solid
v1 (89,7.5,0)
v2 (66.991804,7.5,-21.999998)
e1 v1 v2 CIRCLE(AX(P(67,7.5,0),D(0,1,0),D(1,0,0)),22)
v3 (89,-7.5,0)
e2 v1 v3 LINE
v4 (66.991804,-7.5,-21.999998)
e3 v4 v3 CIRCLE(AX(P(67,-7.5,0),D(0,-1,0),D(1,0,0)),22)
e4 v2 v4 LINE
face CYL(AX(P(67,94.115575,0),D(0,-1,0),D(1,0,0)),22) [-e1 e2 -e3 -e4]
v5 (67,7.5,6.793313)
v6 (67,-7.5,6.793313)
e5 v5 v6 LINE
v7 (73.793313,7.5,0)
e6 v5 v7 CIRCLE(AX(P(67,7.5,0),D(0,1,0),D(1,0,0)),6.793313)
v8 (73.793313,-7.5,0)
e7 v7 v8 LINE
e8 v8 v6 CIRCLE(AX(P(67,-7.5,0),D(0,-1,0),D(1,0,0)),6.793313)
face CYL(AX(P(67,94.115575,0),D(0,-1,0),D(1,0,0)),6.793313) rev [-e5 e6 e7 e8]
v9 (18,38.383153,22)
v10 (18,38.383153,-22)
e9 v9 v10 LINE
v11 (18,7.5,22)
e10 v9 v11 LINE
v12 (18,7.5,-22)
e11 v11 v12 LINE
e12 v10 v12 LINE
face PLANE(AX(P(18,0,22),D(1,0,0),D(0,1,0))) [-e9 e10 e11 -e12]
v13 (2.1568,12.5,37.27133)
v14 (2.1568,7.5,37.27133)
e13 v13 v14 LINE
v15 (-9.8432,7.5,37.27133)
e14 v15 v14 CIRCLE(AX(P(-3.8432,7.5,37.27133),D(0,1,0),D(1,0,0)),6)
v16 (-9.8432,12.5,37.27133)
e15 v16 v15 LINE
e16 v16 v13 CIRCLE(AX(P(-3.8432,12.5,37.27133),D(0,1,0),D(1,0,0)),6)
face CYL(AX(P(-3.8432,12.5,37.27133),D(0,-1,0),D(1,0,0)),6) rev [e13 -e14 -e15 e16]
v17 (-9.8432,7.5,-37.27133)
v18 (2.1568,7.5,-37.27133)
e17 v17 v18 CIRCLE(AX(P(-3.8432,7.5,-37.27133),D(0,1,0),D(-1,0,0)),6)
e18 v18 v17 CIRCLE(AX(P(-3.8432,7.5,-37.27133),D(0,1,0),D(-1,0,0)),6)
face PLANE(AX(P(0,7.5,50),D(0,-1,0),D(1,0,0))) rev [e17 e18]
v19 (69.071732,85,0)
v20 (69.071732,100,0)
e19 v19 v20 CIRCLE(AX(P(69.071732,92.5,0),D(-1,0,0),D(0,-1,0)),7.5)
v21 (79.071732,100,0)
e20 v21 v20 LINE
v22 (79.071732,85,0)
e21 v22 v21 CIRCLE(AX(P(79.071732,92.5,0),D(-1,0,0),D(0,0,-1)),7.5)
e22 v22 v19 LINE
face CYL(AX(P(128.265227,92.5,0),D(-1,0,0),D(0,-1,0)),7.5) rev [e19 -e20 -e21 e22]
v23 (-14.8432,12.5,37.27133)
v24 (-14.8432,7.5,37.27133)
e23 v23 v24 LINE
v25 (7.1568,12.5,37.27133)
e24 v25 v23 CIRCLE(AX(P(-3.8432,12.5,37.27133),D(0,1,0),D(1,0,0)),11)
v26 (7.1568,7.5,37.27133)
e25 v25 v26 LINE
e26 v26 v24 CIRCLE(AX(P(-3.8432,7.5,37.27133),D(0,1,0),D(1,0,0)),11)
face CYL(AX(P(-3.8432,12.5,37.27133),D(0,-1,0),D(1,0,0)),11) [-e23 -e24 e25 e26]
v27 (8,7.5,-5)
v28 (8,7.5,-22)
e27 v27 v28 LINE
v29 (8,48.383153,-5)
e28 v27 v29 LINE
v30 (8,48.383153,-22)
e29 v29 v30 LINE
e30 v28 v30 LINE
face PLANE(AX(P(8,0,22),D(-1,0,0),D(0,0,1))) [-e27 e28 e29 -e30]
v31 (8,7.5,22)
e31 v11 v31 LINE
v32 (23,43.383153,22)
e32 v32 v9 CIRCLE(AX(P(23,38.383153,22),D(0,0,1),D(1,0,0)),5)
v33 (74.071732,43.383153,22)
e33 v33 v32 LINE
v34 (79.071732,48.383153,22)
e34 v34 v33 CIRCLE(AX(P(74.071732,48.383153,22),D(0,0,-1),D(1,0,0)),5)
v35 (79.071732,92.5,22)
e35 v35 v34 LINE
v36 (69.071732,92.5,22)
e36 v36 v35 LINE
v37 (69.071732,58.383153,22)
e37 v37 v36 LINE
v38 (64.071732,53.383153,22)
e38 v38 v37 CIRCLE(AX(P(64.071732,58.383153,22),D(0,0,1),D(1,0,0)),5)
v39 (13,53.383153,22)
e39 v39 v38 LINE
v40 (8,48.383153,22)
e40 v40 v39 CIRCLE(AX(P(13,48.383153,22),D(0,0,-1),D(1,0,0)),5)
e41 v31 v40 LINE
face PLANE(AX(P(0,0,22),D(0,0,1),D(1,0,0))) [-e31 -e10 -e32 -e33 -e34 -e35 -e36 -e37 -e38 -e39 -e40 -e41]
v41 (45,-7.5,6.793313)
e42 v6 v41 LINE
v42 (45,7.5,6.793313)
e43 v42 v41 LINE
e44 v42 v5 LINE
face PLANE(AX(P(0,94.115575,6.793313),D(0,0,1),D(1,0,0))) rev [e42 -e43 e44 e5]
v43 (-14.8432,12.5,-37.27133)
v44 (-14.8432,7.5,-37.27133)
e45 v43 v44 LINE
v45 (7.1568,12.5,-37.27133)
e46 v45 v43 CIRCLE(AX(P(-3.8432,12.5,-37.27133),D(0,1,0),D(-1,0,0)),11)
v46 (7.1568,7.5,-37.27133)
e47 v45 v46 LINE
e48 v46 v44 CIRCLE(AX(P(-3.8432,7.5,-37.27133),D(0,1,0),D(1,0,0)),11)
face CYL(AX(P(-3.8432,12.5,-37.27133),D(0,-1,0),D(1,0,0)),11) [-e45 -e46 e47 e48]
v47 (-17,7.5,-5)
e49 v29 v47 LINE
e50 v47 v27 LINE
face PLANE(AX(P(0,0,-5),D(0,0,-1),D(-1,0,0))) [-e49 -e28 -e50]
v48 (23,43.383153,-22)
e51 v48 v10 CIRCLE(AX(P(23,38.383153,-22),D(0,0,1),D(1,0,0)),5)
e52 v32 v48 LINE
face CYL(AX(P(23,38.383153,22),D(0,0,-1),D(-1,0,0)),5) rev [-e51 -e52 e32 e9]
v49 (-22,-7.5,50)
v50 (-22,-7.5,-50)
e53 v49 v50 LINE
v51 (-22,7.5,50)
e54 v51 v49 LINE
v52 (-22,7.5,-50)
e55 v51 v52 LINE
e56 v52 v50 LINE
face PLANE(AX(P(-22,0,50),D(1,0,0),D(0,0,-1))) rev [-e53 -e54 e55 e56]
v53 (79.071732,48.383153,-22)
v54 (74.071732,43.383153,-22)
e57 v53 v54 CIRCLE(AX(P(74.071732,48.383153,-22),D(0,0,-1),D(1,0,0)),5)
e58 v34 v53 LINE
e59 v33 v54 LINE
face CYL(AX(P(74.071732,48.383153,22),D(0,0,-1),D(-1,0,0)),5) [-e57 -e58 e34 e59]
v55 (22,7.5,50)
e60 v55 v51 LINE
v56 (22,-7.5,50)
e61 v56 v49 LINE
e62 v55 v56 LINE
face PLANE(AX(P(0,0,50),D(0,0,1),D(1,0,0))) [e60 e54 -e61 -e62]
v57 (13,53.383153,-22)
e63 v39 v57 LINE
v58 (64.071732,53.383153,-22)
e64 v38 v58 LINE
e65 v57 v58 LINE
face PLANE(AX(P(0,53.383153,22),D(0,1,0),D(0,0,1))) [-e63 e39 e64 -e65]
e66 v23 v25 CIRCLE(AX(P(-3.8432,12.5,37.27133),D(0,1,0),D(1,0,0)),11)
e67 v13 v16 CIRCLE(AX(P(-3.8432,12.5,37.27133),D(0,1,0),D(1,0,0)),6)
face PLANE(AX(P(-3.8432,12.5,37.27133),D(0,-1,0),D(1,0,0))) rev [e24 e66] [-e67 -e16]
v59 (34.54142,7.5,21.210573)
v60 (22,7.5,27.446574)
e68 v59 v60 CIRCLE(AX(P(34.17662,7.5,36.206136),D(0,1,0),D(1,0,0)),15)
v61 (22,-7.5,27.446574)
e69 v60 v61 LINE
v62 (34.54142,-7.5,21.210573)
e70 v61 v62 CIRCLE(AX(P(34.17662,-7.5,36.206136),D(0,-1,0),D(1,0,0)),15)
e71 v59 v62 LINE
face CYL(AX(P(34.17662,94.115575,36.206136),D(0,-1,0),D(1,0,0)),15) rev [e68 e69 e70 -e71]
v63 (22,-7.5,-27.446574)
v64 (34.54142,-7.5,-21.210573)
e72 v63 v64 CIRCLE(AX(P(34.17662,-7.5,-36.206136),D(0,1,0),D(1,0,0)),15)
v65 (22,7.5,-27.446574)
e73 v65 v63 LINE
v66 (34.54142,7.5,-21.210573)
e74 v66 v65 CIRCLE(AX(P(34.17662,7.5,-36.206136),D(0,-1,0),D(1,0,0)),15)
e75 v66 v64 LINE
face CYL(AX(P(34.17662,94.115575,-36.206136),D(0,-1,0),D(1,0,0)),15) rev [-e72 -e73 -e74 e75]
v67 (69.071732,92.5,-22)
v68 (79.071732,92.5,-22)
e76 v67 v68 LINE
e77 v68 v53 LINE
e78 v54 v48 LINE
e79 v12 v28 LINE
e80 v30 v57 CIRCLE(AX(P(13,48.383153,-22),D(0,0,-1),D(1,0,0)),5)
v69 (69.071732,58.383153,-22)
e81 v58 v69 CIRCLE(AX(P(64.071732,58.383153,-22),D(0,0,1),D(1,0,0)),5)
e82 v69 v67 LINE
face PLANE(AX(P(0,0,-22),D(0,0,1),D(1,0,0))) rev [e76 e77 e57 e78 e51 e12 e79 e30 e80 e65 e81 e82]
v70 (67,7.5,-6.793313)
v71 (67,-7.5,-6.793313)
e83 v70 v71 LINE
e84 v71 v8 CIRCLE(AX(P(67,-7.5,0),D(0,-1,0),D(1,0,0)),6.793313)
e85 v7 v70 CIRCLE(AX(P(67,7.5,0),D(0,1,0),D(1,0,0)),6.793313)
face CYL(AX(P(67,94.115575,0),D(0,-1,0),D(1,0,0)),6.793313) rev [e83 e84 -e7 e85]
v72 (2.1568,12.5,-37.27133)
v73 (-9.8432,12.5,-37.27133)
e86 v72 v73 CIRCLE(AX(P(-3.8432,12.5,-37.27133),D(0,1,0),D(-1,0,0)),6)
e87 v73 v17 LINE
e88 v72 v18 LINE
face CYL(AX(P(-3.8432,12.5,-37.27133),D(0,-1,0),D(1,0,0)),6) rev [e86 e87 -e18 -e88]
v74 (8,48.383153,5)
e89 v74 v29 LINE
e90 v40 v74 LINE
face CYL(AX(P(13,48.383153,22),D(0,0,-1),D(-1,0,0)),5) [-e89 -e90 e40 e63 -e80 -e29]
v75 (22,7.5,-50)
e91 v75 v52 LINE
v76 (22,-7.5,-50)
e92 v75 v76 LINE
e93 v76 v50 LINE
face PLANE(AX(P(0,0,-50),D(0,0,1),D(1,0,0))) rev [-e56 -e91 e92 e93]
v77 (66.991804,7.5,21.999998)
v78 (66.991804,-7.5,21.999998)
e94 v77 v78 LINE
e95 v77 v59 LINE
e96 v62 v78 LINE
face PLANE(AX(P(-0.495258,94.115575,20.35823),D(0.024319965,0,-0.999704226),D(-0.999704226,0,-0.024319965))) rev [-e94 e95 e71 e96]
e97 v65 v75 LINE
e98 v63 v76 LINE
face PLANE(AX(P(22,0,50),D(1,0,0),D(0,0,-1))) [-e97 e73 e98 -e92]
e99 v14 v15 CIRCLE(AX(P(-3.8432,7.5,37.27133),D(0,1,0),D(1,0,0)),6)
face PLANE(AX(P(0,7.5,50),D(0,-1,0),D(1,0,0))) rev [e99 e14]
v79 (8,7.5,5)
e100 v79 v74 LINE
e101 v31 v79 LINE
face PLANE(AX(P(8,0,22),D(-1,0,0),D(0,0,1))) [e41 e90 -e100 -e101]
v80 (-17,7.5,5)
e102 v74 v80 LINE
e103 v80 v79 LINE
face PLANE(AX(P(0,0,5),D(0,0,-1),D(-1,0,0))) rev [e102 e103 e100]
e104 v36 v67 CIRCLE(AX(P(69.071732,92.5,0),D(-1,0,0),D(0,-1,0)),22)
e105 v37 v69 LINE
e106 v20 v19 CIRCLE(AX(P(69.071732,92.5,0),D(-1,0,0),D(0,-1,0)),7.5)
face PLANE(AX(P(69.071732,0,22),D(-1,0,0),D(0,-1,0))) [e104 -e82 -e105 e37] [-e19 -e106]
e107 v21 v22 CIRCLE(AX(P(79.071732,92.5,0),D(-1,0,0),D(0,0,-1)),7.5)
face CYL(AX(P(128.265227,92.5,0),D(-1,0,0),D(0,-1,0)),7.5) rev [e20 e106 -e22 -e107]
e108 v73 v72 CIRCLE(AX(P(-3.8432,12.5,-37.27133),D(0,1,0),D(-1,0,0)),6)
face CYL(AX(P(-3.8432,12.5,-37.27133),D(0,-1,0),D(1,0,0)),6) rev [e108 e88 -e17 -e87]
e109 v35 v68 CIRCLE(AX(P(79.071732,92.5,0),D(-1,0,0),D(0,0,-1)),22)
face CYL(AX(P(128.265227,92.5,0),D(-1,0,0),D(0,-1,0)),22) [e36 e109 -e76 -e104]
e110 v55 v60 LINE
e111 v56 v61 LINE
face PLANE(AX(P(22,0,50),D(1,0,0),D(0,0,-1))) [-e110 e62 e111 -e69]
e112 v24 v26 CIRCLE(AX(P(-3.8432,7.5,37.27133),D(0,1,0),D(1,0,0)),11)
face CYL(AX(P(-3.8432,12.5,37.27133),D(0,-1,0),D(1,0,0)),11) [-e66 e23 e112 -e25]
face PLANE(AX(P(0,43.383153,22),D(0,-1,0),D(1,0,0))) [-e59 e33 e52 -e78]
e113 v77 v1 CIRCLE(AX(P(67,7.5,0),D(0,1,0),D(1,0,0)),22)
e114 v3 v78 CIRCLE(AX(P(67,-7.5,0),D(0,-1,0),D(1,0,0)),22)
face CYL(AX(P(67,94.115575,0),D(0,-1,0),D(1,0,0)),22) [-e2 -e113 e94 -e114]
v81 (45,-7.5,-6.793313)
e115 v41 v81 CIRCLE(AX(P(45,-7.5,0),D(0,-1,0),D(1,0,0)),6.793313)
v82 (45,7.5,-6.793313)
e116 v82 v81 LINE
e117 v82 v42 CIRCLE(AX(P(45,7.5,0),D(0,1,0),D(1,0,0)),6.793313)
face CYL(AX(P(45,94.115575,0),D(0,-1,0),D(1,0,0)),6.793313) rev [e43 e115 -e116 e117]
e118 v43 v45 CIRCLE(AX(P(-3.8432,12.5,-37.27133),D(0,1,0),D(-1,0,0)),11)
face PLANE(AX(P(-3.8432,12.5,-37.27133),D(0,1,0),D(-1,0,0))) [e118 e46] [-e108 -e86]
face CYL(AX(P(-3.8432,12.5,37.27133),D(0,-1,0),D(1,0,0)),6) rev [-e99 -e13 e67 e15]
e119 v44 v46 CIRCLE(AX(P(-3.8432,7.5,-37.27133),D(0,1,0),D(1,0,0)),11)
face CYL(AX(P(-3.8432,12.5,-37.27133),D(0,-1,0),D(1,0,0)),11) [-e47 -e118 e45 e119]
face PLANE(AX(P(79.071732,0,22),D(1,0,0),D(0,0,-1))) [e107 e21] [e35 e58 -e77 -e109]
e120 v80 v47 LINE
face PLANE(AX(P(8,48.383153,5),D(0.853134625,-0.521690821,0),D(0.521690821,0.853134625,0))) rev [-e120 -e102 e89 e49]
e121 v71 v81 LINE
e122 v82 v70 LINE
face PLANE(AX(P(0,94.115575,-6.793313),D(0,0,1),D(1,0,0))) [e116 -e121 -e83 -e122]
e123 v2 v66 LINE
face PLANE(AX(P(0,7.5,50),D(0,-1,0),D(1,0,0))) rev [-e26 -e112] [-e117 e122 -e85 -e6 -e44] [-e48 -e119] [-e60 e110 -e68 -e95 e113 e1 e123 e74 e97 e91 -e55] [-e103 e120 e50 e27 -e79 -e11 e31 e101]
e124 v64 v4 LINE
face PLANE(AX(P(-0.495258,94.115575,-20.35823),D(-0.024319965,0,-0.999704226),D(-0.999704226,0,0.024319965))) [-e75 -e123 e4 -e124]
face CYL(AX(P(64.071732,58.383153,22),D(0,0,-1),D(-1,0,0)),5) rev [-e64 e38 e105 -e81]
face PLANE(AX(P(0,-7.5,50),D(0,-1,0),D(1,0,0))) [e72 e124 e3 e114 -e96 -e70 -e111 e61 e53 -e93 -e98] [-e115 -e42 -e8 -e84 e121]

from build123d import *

# Parameters (mm, degrees)
BRACKET_PROFILE_SKETCH_W = 44
BRACKET_PROFILE_SKETCH_H = 15
BRACKET_BASE_BODY_DEPTH  = 50
UPRIGHT_WEB_DEPTH        = 22
LUG_BOSS_DEPTH           = 10
LUG_HOLE_CUT_DEPTH       = 44
WASHER_BOSS_SKETCH_R     = 11
WASHER_BOSS_SKETCH_R_2   = 6
WASHER_BOSS_22_DEPTH     = 5
WEB_PAD_DEPTH            = 5
SLOTTED_TAB_DEPTH        = 15


with BuildPart() as part:
    # Bracket Profile Sketch → Bracket Base Body (new, symmetric)
    with BuildSketch(Plane.XY):
        Rectangle(BRACKET_PROFILE_SKETCH_W, BRACKET_PROFILE_SKETCH_H)
    extrude(amount=BRACKET_BASE_BODY_DEPTH, both=True)

    # Sketch1_3 → Upright Web (add, symmetric)
    with BuildSketch(Plane.XY):
        with BuildLine():
            Line((8, 7.5), (18, 7.5))
            Line((18, 7.5), (18, 38.383152955))
            ThreePointArc((18, 38.383152955), (19.464466094, 41.91868686), (23, 43.383152955))
            Line((23, 43.383152955), (74.071731591, 43.383152955))
            ThreePointArc((74.071731591, 43.383152955), (77.607265497, 44.847619049), (79.071731591, 48.383152955))
            Line((79.071731591, 48.383152955), (79.071731591, 92.5))
            Line((79.071731591, 92.5), (69.071731591, 92.5))
            Line((69.071731591, 92.5), (69.071731591, 58.383152955))
            ThreePointArc((69.071731591, 58.383152955), (67.607265497, 54.847619049), (64.071731591, 53.383152955))
            Line((64.071731591, 53.383152955), (13, 53.383152955))
            ThreePointArc((13, 53.383152955), (9.464466094, 51.91868686), (8, 48.383152955))
            Line((8, 48.383152955), (8, 7.5))
        make_face()
    extrude(amount=UPRIGHT_WEB_DEPTH, both=True)

    # Lug Profile Sketch → Lug Boss (add)
    with BuildSketch(Plane.ZY.offset(-69.071731591)):
        with BuildLine():
            Line((7.5, 92.5), (22, 92.5))
            ThreePointArc((22, 92.5), (0, 114.5), (-22, 92.5))
            Line((-22, 92.5), (-7.5, 92.5))
            ThreePointArc((-7.5, 92.5), (0, 100), (7.5, 92.5))
        make_face()
    extrude(amount=-LUG_BOSS_DEPTH)

    # Sketch2_3 → Lug Hole Cut (cut)
    with BuildSketch(Plane.ZY.offset(-69.071731591)):
        with BuildLine():
            ThreePointArc((-7.5, 92.5), (0, 85), (7.5, 92.5))
            Line((7.5, 92.5), (-7.5, 92.5))
        make_face()
        with BuildLine():
            Line((-7.5, 92.5), (7.5, 92.5))
            ThreePointArc((7.5, 92.5), (0, 100), (-7.5, 92.5))
        make_face()
    extrude(amount=-LUG_HOLE_CUT_DEPTH, mode=Mode.SUBTRACT)

    # Washer Boss Sketch → Washer Boss _22 (add)
    # profile 1 of 2: a face of its own
    with BuildSketch(Plane(origin=(0, 7.5, 0), x_dir=(1, 0, 0), z_dir=(0, 1, 0))):
        with Locations((-3.843200035, 37.271330251)):
            Circle(WASHER_BOSS_SKETCH_R)
        with Locations(Location((-3.843200035, 37.271330251, 0), (0, 0, 180))):
            Circle(WASHER_BOSS_SKETCH_R_2, mode=Mode.SUBTRACT)
    # profile 2 of 2: a face of its own
    with BuildSketch(Plane(origin=(0, 7.5, 0), x_dir=(1, 0, 0), z_dir=(0, 1, 0))):
        with Locations((-3.843200035, -37.271330251)):
            Circle(WASHER_BOSS_SKETCH_R)
        with Locations((-3.843200035, -37.271330251)):
            Circle(WASHER_BOSS_SKETCH_R_2, mode=Mode.SUBTRACT)
    extrude(amount=WASHER_BOSS_22_DEPTH)

    # Web Pad Sketch → Web Pad (add, symmetric)
    with BuildSketch(Plane.XY):
        Polygon((8, 48.383152955), (-17, 7.5), (8, 7.5), align=None)
    extrude(amount=WEB_PAD_DEPTH, both=True)

    # Slotted Tab Sketch → Slotted Tab (add)
    with BuildSketch(Plane.XZ.offset(7.5)):
        with BuildLine():
            Line((66.991803694, 21.999998473), (34.541419601, 21.210572784))
            ThreePointArc((34.541419601, 21.210572784), (27.498169269, 22.774892965), (22, 27.446574412))
            Line((22, 27.446574412), (22, -27.446574412))
            ThreePointArc((22, -27.446574412), (27.498169269, -22.774892965), (34.541419601, -21.210572784))
            Line((34.541419601, -21.210572784), (66.991803694, -21.999998473))
            ThreePointArc((66.991803694, -21.999998473), (89, 0), (66.991803694, 21.999998473))
        make_face()
        with BuildLine():
            ThreePointArc((67, 6.793312715), (73.793312715, 0), (67, -6.793312715))
            Line((67, -6.793312715), (45, -6.793312715))
            ThreePointArc((45, -6.793312715), (38.206687285, 0), (45, 6.793312715))
            Line((45, 6.793312715), (67, 6.793312715))
        make_face(mode=Mode.SUBTRACT)
    extrude(amount=-SLOTTED_TAB_DEPTH)


solid = part.part
